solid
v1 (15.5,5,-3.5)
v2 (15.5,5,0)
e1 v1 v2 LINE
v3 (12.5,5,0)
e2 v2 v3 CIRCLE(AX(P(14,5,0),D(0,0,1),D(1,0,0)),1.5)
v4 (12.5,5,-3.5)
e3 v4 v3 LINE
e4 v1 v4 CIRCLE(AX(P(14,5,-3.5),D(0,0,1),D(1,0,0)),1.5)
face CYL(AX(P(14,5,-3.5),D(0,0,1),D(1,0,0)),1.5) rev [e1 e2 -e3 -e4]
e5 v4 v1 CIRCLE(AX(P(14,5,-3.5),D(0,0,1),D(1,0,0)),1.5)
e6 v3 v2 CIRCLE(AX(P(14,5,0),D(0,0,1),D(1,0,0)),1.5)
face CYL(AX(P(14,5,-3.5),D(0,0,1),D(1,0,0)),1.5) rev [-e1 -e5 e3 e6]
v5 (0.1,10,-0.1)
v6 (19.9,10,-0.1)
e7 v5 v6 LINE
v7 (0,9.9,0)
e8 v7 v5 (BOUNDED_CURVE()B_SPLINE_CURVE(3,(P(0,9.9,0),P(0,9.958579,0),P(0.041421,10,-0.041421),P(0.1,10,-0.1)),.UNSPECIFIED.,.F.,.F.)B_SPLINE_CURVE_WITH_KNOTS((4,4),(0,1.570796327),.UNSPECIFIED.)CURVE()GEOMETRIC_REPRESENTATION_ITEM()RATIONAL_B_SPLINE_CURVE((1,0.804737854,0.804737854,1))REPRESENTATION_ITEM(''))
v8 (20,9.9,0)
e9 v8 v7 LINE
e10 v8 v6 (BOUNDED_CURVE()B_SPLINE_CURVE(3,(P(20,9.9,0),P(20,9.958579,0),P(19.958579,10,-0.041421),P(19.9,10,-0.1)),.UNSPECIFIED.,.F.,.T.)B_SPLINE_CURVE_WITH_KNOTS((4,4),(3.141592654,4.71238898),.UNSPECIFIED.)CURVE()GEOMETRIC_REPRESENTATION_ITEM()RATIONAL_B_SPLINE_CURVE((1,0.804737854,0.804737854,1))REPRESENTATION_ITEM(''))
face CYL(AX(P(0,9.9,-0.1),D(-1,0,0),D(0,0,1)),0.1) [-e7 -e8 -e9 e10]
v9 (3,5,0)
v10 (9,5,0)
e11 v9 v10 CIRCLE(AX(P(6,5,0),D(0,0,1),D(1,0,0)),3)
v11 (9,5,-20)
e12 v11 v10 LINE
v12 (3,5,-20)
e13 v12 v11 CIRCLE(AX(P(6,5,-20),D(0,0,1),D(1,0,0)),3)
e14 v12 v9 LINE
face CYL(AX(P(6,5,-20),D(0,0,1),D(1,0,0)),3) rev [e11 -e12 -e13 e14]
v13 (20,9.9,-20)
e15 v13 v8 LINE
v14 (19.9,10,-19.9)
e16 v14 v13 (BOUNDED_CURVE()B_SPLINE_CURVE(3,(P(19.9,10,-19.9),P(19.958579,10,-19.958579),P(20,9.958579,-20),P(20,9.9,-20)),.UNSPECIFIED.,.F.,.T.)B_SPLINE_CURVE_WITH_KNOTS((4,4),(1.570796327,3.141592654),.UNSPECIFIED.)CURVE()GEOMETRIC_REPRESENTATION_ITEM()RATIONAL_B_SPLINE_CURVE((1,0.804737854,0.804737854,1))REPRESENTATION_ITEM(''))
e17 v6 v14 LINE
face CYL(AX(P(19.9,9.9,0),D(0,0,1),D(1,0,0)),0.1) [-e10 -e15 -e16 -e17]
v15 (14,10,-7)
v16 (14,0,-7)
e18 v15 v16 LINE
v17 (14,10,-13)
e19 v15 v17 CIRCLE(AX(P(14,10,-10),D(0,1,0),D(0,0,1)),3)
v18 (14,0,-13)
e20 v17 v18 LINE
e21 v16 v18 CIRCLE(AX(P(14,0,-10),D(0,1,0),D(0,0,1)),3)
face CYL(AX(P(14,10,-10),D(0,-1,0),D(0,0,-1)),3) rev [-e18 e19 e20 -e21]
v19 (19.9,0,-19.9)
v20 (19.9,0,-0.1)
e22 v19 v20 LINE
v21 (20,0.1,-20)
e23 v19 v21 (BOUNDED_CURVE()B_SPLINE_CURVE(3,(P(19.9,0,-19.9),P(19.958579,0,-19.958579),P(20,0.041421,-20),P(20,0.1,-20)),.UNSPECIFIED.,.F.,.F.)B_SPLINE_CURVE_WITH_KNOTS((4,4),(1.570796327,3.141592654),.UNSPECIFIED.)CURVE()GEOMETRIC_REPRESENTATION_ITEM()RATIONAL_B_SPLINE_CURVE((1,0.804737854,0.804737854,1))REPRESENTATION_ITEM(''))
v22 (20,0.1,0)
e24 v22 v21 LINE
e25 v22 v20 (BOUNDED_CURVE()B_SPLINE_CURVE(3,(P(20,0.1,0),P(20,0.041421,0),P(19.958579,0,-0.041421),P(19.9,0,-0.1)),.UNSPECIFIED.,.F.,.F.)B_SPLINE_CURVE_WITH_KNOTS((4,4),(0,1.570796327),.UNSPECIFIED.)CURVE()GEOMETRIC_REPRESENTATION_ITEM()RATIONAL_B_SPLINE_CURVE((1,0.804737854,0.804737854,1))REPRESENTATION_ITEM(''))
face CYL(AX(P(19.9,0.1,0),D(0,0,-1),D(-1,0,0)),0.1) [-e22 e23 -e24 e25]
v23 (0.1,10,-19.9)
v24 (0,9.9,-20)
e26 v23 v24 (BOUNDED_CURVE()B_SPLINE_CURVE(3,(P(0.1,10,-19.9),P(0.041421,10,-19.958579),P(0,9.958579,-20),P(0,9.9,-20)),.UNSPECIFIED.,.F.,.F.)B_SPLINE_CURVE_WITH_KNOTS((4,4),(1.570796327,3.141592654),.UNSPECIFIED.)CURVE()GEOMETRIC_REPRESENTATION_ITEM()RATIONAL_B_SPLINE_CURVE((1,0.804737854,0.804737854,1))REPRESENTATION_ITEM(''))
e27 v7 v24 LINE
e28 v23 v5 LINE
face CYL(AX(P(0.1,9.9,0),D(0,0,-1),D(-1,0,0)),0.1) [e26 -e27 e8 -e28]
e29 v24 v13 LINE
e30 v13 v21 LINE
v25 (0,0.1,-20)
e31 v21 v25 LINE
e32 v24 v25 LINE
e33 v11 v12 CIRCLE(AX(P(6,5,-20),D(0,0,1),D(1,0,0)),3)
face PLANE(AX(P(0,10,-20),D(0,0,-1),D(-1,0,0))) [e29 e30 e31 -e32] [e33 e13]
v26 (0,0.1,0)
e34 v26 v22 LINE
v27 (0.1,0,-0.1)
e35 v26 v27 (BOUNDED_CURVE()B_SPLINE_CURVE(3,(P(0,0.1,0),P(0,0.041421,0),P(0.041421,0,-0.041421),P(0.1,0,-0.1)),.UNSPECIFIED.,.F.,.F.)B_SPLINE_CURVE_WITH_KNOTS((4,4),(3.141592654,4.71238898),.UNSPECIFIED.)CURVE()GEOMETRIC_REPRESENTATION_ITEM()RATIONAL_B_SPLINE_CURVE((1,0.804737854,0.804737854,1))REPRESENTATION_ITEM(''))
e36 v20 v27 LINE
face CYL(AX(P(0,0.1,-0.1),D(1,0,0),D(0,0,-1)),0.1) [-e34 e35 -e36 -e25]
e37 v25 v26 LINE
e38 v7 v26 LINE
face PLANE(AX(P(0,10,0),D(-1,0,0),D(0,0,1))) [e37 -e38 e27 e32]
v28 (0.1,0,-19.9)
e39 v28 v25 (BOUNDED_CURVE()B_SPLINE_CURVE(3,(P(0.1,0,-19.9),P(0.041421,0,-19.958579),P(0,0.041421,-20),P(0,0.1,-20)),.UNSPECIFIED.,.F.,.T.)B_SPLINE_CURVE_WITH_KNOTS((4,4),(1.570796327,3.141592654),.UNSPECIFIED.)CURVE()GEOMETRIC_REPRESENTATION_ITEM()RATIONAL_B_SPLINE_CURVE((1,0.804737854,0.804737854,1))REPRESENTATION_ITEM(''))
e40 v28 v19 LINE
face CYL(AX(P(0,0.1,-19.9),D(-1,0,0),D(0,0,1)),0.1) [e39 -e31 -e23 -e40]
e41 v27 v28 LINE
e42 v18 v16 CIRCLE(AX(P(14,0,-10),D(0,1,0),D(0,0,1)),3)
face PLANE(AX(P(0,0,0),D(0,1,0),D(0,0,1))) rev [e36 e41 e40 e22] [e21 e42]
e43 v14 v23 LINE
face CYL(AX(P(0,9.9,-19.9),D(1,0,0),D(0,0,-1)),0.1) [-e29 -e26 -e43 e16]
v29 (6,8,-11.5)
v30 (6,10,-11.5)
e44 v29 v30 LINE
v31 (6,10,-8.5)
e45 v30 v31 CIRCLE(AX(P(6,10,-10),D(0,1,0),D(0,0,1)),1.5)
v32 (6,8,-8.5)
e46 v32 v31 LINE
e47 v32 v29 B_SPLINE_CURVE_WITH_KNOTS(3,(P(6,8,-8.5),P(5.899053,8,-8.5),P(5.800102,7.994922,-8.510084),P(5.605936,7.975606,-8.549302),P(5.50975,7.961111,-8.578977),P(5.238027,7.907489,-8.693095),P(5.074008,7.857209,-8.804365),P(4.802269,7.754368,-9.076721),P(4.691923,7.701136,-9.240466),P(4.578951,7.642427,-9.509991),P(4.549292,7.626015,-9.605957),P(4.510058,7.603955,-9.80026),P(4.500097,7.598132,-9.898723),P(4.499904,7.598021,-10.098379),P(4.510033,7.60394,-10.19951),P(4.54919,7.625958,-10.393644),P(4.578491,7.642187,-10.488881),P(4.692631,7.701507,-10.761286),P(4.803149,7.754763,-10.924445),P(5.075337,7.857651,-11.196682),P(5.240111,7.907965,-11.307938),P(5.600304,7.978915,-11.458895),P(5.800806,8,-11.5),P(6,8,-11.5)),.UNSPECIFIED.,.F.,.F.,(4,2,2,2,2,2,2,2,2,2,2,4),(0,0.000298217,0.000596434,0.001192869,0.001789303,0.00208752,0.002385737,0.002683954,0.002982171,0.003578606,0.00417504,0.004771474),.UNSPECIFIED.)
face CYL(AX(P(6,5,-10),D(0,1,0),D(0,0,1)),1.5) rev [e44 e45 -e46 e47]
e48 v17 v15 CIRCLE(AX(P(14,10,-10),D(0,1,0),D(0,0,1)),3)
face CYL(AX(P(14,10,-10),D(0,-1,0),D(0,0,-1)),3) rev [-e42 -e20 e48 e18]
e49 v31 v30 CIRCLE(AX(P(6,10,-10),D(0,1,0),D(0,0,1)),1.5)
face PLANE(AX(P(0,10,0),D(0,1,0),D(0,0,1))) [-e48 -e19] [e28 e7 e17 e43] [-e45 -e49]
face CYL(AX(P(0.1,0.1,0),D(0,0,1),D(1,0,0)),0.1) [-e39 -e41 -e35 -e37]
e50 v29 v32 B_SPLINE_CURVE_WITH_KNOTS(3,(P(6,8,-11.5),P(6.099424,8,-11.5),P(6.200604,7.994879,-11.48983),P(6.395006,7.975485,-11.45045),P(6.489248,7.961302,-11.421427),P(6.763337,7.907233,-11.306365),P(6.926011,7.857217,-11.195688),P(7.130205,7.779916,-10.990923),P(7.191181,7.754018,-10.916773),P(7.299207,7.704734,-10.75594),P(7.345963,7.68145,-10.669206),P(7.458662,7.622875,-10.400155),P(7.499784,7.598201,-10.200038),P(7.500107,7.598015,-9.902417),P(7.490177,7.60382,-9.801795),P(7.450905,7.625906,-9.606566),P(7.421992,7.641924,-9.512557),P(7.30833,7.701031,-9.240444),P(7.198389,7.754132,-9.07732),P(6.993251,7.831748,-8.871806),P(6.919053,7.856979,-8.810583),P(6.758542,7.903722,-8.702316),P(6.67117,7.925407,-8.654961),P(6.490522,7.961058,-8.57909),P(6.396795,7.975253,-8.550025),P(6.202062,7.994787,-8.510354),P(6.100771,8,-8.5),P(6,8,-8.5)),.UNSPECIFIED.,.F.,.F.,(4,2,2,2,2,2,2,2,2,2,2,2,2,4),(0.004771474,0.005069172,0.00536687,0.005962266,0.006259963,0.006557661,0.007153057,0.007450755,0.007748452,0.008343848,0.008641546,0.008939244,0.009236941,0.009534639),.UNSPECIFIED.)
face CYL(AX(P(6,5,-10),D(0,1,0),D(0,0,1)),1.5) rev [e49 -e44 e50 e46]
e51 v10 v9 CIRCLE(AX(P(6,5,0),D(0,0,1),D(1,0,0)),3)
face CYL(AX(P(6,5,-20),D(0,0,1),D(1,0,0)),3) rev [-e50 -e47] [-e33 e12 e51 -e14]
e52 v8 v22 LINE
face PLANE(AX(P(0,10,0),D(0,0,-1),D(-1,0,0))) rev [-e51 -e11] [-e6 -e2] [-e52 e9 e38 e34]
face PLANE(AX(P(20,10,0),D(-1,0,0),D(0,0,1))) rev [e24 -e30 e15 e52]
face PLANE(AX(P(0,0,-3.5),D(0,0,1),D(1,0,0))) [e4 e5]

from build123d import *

# Parameters (mm, degrees)
SKETCH1_W           = 20
SKETCH1_H           = 20
SKETCH1_R           = 1.5
SKETCH1_R_2         = 3
BOSS_EXTRUDE1_DEPTH = 10
CUT_EXTRUDE5_START  = 10
SKETCH1_3_R         = 1.5
CUT_EXTRUDE5_DEPTH  = 5
SKETCH2_R           = 3
CUT_EXTRUDE1_DEPTH  = 31
SKETCH3_R           = 1.5
CUT_EXTRUDE2_DEPTH  = 3.5
FILLET1_R           = 0.1


with BuildPart() as part:
    # Sketch1 → Boss-Extrude1 (new body)
    # profile 1 of 2: a face of its own
    with BuildSketch(Plane(origin=(0, 0, 0), x_dir=(1, 0, 0), z_dir=(0, 1, 0))):
        with Locations((10, 10)):
            Rectangle(SKETCH1_W, SKETCH1_H)
        with Locations((6, 10)):
            Circle(SKETCH1_R, mode=Mode.SUBTRACT)
        with Locations(Location((14, 10, 0), (0, 0, 270))):
            Circle(SKETCH1_R_2, mode=Mode.SUBTRACT)
    # profile 2 of 2: a face of its own
    with BuildSketch(Plane(origin=(0, 0, 0), x_dir=(1, 0, 0), z_dir=(0, 1, 0))):
        with Locations((6, 10)):
            Circle(SKETCH1_R)
    extrude(amount=BOSS_EXTRUDE1_DEPTH)

    # Sketch1<3> → Cut-Extrude5 (cut)
    with BuildSketch(Plane(origin=(0, 0, 0), x_dir=(1, 0, 0), z_dir=(0, 1, 0)).offset(CUT_EXTRUDE5_START)):
        with Locations(Location((6, 10, 0), (0, 0, 270))):
            Circle(SKETCH1_3_R)
    extrude(amount=-CUT_EXTRUDE5_DEPTH, mode=Mode.SUBTRACT)

    # Sketch2 → Cut-Extrude1 (cut, through all)
    with BuildSketch(Plane.XY):
        with Locations((6, 5)):
            Circle(SKETCH2_R)
    extrude(amount=-CUT_EXTRUDE1_DEPTH, mode=Mode.SUBTRACT)

    # Sketch3 → Cut-Extrude2 (cut)
    with BuildSketch(Plane.XY):
        with Locations((14, 5)):
            Circle(SKETCH3_R)
    extrude(amount=-CUT_EXTRUDE2_DEPTH, mode=Mode.SUBTRACT)

    # Fillet1
    fillet1_edges = [part.edges().sort_by_distance(p)[0] for p in [
        (20, 10, -10),
        (10, 10, -20),
        (0, 10, -10),
        (0, 0, -10),
        (10, 0, -20),
        (20, 0, -10),
        (10, 0, 0),
        (10, 10, 0),
    ]]
    fillet(fillet1_edges, radius=FILLET1_R)


solid = part.part
